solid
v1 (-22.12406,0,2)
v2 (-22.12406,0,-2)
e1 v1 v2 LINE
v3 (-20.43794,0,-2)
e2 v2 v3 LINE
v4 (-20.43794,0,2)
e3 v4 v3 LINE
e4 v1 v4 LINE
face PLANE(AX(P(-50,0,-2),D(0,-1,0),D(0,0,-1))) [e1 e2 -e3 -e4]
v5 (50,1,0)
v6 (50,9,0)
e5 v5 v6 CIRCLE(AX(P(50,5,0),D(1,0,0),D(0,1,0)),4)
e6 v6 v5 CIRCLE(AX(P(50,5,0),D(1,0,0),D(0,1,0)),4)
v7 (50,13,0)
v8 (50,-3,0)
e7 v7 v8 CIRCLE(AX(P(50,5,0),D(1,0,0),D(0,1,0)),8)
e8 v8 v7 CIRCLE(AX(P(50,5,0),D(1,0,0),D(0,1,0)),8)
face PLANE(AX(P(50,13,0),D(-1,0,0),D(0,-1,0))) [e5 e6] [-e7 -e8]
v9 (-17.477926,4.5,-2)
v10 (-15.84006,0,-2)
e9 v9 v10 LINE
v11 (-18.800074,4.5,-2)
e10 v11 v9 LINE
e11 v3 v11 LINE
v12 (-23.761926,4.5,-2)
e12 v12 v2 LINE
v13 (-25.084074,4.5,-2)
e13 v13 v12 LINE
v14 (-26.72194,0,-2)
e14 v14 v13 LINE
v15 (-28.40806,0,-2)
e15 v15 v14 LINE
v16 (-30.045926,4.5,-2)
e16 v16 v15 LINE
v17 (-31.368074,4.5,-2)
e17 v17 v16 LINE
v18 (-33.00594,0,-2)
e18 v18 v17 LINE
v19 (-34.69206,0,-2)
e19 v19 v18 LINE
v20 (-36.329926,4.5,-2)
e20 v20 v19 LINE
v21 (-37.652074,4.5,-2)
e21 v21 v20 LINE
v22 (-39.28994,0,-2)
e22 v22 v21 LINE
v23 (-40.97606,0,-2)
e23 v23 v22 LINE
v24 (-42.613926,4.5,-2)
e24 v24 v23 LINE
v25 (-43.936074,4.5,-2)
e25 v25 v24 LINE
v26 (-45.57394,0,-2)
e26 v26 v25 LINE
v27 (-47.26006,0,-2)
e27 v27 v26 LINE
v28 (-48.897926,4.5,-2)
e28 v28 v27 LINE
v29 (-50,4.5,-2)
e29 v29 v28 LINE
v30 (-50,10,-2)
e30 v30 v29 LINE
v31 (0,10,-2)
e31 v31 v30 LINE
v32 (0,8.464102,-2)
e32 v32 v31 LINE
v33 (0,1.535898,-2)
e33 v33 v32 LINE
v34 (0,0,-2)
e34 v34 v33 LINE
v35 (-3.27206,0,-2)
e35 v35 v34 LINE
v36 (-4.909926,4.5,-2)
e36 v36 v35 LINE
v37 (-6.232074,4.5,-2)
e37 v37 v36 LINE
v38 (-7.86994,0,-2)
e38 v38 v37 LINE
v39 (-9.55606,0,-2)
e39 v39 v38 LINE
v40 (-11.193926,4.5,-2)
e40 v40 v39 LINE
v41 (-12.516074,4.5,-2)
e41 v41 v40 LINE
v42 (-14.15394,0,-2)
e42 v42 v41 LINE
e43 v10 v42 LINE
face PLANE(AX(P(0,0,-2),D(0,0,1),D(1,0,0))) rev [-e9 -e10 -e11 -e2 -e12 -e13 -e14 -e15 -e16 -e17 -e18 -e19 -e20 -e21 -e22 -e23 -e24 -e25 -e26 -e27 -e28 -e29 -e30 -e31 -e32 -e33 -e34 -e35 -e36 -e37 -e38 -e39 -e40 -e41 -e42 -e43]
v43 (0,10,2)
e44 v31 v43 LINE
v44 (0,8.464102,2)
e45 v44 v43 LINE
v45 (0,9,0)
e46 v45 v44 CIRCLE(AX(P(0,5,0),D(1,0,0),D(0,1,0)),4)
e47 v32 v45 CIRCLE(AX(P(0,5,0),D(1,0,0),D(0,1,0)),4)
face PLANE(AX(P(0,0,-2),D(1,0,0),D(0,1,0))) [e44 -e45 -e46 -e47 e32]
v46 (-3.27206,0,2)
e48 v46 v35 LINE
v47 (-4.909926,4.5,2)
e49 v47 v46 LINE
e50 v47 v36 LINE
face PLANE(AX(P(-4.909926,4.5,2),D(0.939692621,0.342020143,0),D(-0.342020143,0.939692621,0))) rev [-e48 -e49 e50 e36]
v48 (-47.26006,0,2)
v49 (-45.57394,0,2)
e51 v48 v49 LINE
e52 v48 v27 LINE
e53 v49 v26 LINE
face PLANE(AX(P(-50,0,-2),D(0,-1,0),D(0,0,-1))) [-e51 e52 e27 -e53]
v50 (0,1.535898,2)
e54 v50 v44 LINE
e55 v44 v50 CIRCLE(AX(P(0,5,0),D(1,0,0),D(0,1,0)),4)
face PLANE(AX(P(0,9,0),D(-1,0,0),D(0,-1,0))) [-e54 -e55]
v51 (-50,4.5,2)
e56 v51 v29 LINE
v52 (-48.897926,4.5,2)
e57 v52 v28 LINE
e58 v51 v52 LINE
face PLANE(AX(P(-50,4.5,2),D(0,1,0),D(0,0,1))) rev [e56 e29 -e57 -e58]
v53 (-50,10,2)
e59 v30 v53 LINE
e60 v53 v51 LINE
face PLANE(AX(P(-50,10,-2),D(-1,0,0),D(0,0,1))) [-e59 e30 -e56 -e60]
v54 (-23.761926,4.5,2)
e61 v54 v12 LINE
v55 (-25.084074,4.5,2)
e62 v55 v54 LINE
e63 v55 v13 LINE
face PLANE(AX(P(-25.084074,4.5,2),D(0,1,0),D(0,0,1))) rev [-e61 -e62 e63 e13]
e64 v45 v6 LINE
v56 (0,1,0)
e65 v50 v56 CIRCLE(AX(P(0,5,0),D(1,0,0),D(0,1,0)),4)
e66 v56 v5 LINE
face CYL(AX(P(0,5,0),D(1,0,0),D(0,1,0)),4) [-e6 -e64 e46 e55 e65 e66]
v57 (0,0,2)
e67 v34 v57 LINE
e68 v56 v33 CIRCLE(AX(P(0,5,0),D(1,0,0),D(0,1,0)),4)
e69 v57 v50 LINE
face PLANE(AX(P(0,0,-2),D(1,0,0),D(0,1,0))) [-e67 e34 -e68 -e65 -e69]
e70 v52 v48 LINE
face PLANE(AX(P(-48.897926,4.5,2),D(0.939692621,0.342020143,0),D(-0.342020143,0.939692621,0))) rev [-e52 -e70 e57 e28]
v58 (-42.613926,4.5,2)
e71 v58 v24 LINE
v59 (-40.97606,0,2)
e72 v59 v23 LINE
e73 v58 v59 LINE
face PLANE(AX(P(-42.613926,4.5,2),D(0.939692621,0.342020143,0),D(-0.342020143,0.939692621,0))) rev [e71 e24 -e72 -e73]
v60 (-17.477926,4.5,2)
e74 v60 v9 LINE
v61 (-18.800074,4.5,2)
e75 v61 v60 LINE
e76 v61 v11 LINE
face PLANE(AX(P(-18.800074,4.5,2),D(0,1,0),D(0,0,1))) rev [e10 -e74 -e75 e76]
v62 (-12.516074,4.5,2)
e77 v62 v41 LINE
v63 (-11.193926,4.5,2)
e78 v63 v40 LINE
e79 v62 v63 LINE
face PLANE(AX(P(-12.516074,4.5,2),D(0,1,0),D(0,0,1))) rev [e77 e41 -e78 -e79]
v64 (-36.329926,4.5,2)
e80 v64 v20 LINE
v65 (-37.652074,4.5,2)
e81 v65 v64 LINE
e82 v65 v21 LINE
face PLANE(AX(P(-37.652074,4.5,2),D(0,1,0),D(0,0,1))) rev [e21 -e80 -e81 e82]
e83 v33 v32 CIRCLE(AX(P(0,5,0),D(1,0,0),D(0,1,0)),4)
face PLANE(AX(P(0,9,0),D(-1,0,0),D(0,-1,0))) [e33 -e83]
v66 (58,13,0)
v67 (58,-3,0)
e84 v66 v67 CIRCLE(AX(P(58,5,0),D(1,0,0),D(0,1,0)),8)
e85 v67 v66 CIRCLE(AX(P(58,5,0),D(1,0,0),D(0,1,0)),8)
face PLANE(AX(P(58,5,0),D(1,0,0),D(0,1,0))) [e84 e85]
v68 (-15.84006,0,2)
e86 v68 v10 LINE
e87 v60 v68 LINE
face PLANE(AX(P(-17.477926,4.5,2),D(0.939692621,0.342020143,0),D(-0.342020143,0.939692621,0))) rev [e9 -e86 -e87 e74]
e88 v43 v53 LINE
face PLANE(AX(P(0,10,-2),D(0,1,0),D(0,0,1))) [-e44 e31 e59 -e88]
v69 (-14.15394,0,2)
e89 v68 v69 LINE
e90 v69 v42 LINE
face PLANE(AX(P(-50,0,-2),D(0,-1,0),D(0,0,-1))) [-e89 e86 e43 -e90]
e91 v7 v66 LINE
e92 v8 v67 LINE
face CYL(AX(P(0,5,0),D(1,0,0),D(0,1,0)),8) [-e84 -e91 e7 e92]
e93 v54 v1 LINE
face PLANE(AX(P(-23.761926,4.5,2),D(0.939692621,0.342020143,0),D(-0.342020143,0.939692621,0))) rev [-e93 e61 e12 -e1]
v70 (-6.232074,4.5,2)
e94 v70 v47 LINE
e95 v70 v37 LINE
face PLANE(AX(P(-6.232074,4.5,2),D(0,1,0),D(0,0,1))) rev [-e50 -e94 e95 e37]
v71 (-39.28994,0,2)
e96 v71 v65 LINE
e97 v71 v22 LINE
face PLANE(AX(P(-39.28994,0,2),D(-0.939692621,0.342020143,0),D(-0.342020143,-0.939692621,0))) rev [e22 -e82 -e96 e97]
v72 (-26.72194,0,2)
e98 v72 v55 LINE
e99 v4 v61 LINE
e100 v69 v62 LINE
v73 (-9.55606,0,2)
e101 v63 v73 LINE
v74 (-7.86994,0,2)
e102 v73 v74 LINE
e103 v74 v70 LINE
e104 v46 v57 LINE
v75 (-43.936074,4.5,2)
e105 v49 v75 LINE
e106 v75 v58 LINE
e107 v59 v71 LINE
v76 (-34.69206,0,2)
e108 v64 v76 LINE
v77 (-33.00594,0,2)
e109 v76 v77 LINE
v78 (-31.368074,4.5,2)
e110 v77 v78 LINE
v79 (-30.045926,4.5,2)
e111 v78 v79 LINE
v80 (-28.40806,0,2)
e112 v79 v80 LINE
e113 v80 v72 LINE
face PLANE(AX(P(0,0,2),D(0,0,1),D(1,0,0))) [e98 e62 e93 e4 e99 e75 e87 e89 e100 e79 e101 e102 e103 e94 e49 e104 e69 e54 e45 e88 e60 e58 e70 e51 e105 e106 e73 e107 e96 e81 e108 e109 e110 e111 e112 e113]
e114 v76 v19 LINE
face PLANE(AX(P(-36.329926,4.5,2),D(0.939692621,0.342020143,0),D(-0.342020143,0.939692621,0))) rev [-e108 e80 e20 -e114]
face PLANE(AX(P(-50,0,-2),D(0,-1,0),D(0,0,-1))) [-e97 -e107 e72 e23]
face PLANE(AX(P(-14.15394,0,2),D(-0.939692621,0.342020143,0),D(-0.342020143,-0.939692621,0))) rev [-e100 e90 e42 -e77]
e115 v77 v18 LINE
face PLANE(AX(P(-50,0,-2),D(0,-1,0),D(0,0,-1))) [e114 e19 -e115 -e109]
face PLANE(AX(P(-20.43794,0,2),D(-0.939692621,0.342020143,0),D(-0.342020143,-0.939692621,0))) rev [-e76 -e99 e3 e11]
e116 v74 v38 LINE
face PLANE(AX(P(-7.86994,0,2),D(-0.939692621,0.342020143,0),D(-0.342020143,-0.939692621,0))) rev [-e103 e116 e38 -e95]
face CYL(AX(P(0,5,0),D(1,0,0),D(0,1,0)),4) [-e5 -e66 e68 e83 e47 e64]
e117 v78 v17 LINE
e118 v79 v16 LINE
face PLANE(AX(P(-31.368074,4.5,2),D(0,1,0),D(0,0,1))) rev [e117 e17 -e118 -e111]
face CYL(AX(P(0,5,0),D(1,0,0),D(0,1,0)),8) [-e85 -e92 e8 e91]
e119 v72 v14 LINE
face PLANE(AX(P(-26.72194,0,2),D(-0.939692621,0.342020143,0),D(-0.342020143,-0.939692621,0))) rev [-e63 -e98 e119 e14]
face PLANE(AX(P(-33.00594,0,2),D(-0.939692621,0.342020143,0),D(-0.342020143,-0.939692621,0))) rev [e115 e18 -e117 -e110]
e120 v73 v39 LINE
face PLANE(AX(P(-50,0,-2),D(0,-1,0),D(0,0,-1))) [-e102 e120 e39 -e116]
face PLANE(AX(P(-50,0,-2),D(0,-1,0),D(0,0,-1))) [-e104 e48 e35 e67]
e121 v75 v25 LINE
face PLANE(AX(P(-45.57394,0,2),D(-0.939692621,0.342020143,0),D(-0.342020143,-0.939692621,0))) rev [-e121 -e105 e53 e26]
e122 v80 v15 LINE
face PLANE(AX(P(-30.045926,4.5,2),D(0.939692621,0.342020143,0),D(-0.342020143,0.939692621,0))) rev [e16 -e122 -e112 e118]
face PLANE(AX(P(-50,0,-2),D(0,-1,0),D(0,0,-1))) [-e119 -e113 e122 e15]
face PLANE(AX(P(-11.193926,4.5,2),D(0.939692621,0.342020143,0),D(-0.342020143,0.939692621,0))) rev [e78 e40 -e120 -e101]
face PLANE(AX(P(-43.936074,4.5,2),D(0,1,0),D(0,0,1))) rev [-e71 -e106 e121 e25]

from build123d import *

# Parameters (mm, degrees)
SKETCH1_W           = 50
SKETCH1_H           = 10
BOSS_EXTRUDE1_DEPTH = 4
CUT_EXTRUDE1_DEPTH  = 52.14684741
CUT_EXTRUDE2_DEPTH  = 52.14684741
CUT_EXTRUDE3_DEPTH  = 52.14684741
CUT_EXTRUDE4_DEPTH  = 52.14684741
CUT_EXTRUDE5_DEPTH  = 52.14684741
CUT_EXTRUDE6_DEPTH  = 52.14684741
CUT_EXTRUDE7_DEPTH  = 52.14684741
CUT_EXTRUDE8_DEPTH  = 52.14684741


with BuildPart() as part:
    # Sketch1 → Boss-Extrude1 (new body)
    with BuildSketch(Plane.XY.offset(2)):
        with Locations((-25, 5)):
            Rectangle(SKETCH1_W, SKETCH1_H)
    extrude(amount=-BOSS_EXTRUDE1_DEPTH)

    # Sketch2 → Cut-Extrude1 (cut, through all)
    with BuildSketch(Plane(origin=(0, 0, -2), x_dir=(-1, 0, 0), z_dir=(0, 0, -1))):
        Polygon((40.976059531, 0), (45.573940469, 0), (43.936074414, 4.5), (42.613925586, 4.5), align=None)
    extrude(amount=-CUT_EXTRUDE1_DEPTH, mode=Mode.SUBTRACT)

    # Sketch3 → Cut-Extrude2 (cut, through all)
    with BuildSketch(Plane(origin=(0, 0, -2), x_dir=(-1, 0, 0), z_dir=(0, 0, -1))):
        Polygon((34.692059531, 0), (39.289940469, 0), (37.652074414, 4.5), (36.329925586, 4.5), align=None)
    extrude(amount=-CUT_EXTRUDE2_DEPTH, mode=Mode.SUBTRACT)

    # Sketch4 → Cut-Extrude3 (cut, through all)
    with BuildSketch(Plane(origin=(0, 0, -2), x_dir=(-1, 0, 0), z_dir=(0, 0, -1))):
        Polygon((28.408059531, 0), (33.005940469, 0), (31.368074414, 4.5), (30.045925586, 4.5), align=None)
    extrude(amount=-CUT_EXTRUDE3_DEPTH, mode=Mode.SUBTRACT)

    # Sketch5 → Cut-Extrude4 (cut, through all)
    with BuildSketch(Plane(origin=(0, 0, -2), x_dir=(-1, 0, 0), z_dir=(0, 0, -1))):
        Polygon((22.124059531, 0), (26.721940469, 0), (25.084074414, 4.5), (23.761925586, 4.5), align=None)
    extrude(amount=-CUT_EXTRUDE4_DEPTH, mode=Mode.SUBTRACT)

    # Sketch6 → Cut-Extrude5 (cut, through all)
    with BuildSketch(Plane(origin=(0, 0, -2), x_dir=(-1, 0, 0), z_dir=(0, 0, -1))):
        Polygon((15.840059531, 0), (20.437940469, 0), (18.800074414, 4.5), (17.477925586, 4.5), align=None)
    extrude(amount=-CUT_EXTRUDE5_DEPTH, mode=Mode.SUBTRACT)

    # Sketch7 → Cut-Extrude6 (cut, through all)
    with BuildSketch(Plane(origin=(0, 0, -2), x_dir=(-1, 0, 0), z_dir=(0, 0, -1))):
        Polygon((9.556059531, 0), (14.153940469, 0), (12.516074414, 4.5), (11.193925586, 4.5), align=None)
    extrude(amount=-CUT_EXTRUDE6_DEPTH, mode=Mode.SUBTRACT)

    # Sketch8 → Cut-Extrude7 (cut, through all)
    with BuildSketch(Plane(origin=(0, 0, -2), x_dir=(-1, 0, 0), z_dir=(0, 0, -1))):
        Polygon((3.272059531, 0), (7.869940469, 0), (6.232074414, 4.5), (4.909925586, 4.5), align=None)
    extrude(amount=-CUT_EXTRUDE7_DEPTH, mode=Mode.SUBTRACT)

    # Sketch9 → Cut-Extrude8 (cut, through all)
    with BuildSketch(Plane(origin=(0, 0, -2), x_dir=(-1, 0, 0), z_dir=(0, 0, -1))):
        Polygon((48.897925586, 4.5), (47.260059531, 0), (50, 0), (50, 4.5), align=None)
    extrude(amount=-CUT_EXTRUDE8_DEPTH, mode=Mode.SUBTRACT)

    # Sketch10 → Revolve1 (revolve)
    with BuildSketch(Plane.XY):
        Polygon((0, 9), (0, 5), (58, 5), (58, 13), (50, 13), (50, 9), align=None)
    revolve(axis=Axis((0, 5, 0), (1, 0, 0)))


solid = part.part
